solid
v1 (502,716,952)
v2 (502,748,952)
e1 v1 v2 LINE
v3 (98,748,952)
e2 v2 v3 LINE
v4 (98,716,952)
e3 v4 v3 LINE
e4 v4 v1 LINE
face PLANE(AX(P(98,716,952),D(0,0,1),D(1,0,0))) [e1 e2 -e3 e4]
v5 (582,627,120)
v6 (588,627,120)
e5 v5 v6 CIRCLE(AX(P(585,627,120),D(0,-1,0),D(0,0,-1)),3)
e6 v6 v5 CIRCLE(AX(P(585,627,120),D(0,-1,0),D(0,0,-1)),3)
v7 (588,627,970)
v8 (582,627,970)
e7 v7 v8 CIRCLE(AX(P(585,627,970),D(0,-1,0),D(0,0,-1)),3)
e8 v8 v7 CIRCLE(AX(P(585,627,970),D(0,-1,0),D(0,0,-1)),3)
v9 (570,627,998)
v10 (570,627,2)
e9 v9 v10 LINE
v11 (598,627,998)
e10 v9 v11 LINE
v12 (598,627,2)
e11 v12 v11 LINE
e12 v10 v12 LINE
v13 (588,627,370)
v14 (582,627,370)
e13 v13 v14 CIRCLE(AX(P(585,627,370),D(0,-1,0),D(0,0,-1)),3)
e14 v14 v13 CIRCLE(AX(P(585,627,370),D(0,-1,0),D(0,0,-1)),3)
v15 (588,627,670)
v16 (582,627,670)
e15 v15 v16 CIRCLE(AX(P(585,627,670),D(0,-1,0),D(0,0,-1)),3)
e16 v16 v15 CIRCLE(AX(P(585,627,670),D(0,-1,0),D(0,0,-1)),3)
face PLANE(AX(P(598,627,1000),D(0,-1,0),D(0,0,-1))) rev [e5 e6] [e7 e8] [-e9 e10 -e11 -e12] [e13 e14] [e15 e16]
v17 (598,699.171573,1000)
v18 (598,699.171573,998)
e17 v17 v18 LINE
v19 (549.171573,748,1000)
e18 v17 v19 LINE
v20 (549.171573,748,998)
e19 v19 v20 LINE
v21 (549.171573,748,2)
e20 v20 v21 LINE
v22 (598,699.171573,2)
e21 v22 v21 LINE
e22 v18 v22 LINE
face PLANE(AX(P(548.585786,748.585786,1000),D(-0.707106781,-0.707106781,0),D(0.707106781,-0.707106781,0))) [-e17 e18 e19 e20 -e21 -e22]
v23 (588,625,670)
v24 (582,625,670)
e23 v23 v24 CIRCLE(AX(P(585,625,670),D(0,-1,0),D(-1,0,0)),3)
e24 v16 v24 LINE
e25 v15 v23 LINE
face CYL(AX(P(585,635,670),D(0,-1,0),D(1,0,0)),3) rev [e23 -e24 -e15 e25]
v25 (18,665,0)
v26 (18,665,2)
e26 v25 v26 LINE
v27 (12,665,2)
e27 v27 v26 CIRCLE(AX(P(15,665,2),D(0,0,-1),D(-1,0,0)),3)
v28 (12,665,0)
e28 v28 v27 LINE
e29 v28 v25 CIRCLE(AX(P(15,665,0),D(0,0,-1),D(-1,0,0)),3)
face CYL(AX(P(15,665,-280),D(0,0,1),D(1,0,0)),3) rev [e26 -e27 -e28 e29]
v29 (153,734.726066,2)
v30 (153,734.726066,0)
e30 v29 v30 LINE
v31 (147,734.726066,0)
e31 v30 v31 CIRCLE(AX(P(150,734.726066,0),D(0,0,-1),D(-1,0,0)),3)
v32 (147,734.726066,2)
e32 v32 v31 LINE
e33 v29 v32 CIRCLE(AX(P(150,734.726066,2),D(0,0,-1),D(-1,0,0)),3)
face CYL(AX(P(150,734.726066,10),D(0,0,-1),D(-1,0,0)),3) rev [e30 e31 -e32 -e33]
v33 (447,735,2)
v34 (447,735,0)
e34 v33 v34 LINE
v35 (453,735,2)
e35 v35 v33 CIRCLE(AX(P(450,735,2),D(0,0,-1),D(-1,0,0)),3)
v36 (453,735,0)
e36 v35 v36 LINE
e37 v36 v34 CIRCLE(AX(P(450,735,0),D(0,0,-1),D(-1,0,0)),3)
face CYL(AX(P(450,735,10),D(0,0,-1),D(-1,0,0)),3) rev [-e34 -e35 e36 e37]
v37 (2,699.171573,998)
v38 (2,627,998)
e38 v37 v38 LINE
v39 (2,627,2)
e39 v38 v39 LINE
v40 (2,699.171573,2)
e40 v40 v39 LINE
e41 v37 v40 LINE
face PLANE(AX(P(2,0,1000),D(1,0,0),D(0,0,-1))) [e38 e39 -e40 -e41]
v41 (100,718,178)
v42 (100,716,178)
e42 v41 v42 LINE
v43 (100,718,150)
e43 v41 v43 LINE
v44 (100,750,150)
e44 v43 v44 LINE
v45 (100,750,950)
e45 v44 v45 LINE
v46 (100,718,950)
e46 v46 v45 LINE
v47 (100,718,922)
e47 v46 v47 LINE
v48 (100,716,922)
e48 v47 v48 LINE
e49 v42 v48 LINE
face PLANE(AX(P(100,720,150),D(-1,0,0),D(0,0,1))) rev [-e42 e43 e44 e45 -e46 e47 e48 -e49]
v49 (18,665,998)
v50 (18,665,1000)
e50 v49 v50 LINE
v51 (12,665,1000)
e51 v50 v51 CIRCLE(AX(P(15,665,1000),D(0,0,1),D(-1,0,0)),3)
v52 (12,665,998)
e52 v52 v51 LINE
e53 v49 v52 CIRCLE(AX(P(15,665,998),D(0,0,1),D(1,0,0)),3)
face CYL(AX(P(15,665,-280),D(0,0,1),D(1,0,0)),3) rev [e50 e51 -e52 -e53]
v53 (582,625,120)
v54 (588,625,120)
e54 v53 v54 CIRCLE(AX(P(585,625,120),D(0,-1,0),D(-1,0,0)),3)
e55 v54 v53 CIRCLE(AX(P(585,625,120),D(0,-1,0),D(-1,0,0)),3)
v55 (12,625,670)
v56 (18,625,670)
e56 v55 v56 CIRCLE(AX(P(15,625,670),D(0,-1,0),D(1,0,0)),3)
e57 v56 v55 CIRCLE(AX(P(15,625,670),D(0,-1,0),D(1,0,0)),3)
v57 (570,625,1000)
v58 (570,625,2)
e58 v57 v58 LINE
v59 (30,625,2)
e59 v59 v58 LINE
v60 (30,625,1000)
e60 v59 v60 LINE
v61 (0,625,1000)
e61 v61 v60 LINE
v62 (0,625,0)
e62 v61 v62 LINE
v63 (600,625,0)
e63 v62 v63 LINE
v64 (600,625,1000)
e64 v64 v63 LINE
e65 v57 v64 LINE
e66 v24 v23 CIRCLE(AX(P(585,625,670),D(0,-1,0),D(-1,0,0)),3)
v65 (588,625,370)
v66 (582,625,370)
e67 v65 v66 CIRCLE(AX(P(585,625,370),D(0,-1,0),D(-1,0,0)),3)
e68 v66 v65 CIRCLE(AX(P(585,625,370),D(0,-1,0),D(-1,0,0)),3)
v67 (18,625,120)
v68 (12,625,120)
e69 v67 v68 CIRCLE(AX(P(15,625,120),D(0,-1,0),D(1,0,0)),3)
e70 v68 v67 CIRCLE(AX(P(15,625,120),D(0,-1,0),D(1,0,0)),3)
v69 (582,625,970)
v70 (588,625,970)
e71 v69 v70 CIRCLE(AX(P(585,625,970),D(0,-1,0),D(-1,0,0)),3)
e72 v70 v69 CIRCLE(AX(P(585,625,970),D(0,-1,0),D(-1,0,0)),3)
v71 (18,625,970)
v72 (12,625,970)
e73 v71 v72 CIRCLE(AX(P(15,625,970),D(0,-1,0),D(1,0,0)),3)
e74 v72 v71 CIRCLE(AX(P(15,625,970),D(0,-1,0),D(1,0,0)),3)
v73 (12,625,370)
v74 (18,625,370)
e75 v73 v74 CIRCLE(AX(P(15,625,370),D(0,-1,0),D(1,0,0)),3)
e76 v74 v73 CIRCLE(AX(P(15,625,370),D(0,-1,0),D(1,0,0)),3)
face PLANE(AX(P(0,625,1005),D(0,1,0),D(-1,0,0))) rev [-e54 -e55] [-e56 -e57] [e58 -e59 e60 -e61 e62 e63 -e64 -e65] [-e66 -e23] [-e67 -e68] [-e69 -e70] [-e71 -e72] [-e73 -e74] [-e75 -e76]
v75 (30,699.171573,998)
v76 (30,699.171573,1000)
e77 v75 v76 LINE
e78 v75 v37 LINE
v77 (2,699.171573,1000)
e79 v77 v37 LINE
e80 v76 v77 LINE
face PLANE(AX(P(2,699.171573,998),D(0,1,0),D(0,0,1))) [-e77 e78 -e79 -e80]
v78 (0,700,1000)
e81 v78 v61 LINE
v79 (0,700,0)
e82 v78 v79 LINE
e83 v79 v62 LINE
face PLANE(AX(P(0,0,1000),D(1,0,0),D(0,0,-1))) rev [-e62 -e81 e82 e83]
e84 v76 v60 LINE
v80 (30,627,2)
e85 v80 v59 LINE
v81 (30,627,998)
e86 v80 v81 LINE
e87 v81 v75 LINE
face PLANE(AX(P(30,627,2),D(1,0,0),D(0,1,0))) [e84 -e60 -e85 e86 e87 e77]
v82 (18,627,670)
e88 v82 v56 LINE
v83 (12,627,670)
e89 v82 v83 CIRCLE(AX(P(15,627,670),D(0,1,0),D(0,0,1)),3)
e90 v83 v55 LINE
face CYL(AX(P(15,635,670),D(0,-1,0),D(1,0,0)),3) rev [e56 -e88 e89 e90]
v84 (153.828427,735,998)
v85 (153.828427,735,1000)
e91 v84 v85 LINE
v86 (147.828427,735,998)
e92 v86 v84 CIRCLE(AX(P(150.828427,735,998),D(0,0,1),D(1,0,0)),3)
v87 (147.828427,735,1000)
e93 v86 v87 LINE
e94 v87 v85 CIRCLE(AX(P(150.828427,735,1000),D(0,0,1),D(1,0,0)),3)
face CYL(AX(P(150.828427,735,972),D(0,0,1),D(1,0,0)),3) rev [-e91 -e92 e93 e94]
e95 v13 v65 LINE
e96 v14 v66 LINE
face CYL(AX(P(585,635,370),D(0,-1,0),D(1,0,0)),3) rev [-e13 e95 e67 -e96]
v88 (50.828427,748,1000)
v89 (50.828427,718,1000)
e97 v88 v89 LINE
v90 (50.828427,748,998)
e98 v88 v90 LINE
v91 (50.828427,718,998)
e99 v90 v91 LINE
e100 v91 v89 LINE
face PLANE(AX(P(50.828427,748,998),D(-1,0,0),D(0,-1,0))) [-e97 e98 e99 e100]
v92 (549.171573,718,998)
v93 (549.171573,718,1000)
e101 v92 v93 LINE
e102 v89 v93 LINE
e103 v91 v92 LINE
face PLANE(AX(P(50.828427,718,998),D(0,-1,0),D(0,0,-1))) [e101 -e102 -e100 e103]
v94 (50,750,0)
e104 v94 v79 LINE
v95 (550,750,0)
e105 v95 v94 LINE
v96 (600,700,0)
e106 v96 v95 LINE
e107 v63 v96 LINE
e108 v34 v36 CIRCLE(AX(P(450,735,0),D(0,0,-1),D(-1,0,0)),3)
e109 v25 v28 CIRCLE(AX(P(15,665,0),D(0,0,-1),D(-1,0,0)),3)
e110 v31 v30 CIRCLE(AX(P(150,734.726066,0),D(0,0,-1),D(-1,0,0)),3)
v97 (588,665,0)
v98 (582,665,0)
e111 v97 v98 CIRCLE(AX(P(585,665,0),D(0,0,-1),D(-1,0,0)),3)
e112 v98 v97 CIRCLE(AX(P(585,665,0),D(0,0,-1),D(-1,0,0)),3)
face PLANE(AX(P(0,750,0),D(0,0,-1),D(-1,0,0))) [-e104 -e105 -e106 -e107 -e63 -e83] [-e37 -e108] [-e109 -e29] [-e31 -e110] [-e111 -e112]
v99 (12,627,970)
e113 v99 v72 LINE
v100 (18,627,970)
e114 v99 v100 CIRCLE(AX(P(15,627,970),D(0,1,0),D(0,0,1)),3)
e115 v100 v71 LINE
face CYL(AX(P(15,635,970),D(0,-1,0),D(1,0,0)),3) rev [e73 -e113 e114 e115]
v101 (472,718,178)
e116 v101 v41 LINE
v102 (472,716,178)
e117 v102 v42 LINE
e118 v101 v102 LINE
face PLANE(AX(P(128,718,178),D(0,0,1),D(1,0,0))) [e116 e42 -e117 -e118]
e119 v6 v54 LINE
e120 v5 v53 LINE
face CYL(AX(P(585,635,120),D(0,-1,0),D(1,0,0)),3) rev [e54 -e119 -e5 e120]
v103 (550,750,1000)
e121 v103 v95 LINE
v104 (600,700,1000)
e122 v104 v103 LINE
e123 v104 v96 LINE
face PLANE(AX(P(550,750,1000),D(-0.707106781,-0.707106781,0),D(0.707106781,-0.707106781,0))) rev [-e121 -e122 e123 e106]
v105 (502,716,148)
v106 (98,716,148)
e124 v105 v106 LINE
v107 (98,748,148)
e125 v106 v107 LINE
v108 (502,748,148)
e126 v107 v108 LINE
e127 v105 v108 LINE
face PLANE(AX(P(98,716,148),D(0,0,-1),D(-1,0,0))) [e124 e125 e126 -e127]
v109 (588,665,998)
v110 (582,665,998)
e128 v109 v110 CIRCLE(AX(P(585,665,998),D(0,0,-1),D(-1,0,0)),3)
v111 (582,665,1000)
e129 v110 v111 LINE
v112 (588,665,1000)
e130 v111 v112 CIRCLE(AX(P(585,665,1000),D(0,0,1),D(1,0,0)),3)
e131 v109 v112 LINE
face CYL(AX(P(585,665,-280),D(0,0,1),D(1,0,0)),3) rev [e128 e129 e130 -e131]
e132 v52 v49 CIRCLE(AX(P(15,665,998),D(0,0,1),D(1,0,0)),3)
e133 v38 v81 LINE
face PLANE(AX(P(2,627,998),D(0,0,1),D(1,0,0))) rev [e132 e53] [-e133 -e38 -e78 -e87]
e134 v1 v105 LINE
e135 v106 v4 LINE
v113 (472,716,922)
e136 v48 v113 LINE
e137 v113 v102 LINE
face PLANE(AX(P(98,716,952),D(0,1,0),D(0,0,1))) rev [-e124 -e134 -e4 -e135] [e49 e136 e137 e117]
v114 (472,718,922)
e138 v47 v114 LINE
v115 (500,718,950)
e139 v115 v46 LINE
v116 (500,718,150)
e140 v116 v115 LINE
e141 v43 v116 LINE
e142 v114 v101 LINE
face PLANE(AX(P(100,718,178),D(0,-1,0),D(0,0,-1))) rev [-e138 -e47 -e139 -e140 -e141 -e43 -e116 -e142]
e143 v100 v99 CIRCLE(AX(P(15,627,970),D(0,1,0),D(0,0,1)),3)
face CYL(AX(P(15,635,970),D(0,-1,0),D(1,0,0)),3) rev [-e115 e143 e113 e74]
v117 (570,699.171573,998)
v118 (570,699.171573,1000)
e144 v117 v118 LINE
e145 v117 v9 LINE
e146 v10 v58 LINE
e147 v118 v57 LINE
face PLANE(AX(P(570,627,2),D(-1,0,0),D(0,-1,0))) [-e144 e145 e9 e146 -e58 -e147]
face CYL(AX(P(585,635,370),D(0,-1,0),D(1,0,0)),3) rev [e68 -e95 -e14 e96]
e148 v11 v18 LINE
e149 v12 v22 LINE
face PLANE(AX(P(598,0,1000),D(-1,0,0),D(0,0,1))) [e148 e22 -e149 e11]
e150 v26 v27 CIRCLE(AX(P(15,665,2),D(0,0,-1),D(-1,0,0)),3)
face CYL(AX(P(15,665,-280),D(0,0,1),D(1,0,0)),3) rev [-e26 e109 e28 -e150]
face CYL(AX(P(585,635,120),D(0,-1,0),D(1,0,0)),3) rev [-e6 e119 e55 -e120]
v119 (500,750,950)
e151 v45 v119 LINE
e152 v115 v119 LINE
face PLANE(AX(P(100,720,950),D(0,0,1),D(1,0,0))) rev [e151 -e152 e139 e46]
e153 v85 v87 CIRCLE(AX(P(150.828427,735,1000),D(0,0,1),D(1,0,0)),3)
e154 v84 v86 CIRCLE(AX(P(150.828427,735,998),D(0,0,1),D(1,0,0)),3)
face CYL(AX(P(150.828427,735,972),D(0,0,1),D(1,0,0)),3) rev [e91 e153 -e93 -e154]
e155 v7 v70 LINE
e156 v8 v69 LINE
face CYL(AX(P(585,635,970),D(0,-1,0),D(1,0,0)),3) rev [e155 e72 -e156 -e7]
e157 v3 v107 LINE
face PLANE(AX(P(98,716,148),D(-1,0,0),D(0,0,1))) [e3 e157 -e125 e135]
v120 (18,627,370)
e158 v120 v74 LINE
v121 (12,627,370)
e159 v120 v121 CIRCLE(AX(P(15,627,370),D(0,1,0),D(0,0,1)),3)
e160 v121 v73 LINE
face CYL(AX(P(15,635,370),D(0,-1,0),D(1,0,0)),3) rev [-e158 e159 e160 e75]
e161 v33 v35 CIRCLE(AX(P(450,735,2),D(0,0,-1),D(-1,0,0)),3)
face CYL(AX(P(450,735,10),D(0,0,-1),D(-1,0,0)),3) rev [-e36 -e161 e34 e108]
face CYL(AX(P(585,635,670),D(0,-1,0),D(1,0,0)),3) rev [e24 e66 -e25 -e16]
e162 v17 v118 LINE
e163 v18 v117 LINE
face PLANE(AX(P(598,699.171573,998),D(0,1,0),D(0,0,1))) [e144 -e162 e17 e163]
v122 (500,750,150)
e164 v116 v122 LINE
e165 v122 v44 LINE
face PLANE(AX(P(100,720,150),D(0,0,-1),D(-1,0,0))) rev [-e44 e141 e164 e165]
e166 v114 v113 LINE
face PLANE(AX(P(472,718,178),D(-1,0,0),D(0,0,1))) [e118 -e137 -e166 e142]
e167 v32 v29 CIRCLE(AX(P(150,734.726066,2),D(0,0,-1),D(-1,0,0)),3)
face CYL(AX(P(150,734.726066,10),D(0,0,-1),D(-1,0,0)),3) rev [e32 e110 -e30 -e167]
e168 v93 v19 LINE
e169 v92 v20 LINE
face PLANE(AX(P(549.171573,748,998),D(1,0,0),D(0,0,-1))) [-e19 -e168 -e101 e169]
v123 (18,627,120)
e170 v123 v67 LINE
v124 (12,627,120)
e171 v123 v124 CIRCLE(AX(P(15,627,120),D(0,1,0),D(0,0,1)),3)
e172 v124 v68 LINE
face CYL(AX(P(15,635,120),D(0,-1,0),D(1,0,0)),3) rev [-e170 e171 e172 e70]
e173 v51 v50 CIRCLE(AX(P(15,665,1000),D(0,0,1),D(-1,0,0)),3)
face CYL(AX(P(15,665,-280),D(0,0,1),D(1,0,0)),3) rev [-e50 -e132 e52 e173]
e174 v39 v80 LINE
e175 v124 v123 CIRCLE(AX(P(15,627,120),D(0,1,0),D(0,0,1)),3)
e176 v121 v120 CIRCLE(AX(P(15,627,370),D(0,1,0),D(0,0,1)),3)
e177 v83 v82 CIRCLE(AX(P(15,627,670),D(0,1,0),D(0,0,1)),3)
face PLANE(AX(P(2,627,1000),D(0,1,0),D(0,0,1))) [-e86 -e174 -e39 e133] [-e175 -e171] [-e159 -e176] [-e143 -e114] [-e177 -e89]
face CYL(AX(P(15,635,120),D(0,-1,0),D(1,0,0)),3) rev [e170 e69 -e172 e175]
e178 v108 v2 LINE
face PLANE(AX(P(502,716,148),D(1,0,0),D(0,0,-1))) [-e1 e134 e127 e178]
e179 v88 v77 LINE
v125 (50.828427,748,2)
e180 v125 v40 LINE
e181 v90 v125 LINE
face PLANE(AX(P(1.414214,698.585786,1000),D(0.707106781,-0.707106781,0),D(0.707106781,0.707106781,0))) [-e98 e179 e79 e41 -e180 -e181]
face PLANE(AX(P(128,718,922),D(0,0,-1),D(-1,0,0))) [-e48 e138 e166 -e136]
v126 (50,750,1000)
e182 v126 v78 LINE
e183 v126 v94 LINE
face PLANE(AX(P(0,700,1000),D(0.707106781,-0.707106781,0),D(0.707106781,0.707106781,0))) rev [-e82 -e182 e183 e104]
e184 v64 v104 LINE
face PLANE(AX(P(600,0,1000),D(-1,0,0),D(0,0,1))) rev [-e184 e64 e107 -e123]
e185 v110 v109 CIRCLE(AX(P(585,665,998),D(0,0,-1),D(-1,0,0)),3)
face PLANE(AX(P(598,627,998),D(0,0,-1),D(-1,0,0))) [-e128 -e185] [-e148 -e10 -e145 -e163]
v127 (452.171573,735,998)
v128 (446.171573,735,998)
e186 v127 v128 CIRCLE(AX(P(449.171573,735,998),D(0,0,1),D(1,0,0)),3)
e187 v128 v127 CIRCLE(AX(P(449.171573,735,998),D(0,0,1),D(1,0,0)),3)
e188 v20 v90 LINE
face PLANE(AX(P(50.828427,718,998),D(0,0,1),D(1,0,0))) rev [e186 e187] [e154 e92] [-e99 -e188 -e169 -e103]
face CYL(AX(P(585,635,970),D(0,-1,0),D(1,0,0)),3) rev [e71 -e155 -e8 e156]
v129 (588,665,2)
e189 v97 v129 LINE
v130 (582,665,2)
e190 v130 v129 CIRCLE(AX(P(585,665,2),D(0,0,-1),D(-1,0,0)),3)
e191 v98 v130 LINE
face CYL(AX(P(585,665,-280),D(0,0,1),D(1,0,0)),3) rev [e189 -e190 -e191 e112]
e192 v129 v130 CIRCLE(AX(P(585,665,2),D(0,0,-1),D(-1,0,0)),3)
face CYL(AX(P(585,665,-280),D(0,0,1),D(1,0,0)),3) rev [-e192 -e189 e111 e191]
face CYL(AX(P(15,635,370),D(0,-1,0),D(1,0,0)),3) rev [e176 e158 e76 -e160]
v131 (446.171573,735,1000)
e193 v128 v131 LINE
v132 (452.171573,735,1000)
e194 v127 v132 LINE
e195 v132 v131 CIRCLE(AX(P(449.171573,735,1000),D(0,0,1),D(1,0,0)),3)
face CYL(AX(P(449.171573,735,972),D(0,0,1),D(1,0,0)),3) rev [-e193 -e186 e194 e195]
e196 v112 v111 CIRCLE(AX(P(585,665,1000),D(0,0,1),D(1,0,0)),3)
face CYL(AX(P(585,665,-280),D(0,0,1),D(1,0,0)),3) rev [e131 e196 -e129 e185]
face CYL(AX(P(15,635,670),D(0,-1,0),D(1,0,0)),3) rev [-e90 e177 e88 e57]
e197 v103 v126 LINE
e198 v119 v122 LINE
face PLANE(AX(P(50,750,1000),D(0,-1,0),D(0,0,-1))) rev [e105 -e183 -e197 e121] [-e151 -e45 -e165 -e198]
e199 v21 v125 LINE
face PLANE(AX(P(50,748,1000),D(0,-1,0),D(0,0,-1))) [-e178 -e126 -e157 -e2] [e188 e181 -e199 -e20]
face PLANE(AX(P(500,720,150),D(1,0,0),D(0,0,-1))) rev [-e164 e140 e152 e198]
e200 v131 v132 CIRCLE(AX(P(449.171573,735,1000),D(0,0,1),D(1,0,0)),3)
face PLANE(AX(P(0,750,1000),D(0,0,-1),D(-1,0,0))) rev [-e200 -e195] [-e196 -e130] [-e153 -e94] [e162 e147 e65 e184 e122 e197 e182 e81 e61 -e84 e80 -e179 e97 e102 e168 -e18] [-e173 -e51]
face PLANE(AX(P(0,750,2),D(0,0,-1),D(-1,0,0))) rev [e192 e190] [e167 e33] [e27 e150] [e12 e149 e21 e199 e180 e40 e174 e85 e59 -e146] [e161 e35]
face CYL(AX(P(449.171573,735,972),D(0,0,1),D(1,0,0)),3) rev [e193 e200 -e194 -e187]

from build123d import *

# Parameters (mm, degrees)
EXTRUDE_1_DEPTH     = 1000
SHELL_1_T           = -2
SKETCH_3_W          = 400
SKETCH_3_H          = 800
CUT_EXTRUDE_1_DEPTH = 30
SKETCH_4_W          = 404
SKETCH_4_H          = 804
SKETCH_4_W_2        = 400
SKETCH_4_H_2        = 800
EXTRUDE_2_DEPTH     = 34
EXTRUDE_3_DEPTH     = 2
SKETCH_6_W          = 600
SKETCH_6_H          = 200
CUT_EXTRUDE_2_DEPTH = 1044
SKETCH_10_W         = 600
SKETCH_10_H         = 425
CUT_EXTRUDE_4_DEPTH = 1005
SKETCH_11_W         = 28
SKETCH_11_H         = 998
EXTRUDE_5_DEPTH     = 2
SKETCH_12_W         = 498.34314575
SKETCH_12_H         = 30
SKETCH_12_W_2       = 28
SKETCH_12_H_2       = 72.171572875
EXTRUDE_6_DEPTH     = 2
SKETCH_13_R         = 3
CUT_EXTRUDE_5_DEPTH = 1280
SKETCH_14_R         = 3
CUT_EXTRUDE_6_DEPTH = 10
SKETCH_15_R         = 3
CUT_EXTRUDE_7_DEPTH = 28
SKETCH_16_R         = 3
CUT_EXTRUDE_8_DEPTH = 10


with BuildPart() as part:
    # 草图1 → 凸台-拉伸1 (new body)
    with BuildSketch(Plane.XY):
        Polygon((0, 700), (50, 750), (550, 750), (600, 700), (600, 0), (0, 0), align=None)
    extrude(amount=EXTRUDE_1_DEPTH)

    # 抽壳1
    shell_1_openings = [part.faces().sort_by_distance(p)[0] for p in [
        (300, 372.998137803, 1000),
    ]]
    offset(amount=SHELL_1_T, openings=shell_1_openings, kind=Kind.INTERSECTION)

    # 草图3 → 切除-拉伸1 (cut)
    with BuildSketch(Plane(origin=(0, 750, 0), x_dir=(1, 0, 0), z_dir=(0, 1, 0))):
        with Locations((300, -550)):
            Rectangle(SKETCH_3_W, SKETCH_3_H)
    extrude(amount=-CUT_EXTRUDE_1_DEPTH, mode=Mode.SUBTRACT)

    # 草图4 → 凸台-拉伸2 (add)
    with BuildSketch(Plane(origin=(0, 750, 0), x_dir=(1, 0, 0), z_dir=(0, 1, 0))):
        with Locations((300, -550)):
            Rectangle(SKETCH_4_W, SKETCH_4_H)
        with Locations((300, -550)):
            Rectangle(SKETCH_4_W_2, SKETCH_4_H_2, mode=Mode.SUBTRACT)
    extrude(amount=-EXTRUDE_2_DEPTH)

    # 草图5 → 凸台-拉伸3 (add)
    with BuildSketch(Plane.XZ.offset(-716)):
        Polygon((128, 178), (472, 178), (472, 922), (128, 922), (100, 922), (100, 950), (500, 950), (500, 150), (100, 150), (100, 178), align=None)
    extrude(amount=-EXTRUDE_3_DEPTH)

    # 草图6 → 切除-拉伸2 (cut)
    with BuildSketch(Plane(origin=(0, 0, 0), x_dir=(-1, 0, 0), z_dir=(0, 0, -1))):
        with Locations((-300, 100)):
            Rectangle(SKETCH_6_W, SKETCH_6_H)
    extrude(amount=-CUT_EXTRUDE_2_DEPTH, mode=Mode.SUBTRACT)

    # 草图10 → 切除-拉伸4 (cut)
    with BuildSketch(Plane(origin=(0, 0, 0), x_dir=(-1, 0, 0), z_dir=(0, 0, -1))):
        with Locations((-300, 412.5)):
            Rectangle(SKETCH_10_W, SKETCH_10_H)
    extrude(amount=-CUT_EXTRUDE_4_DEPTH, mode=Mode.SUBTRACT)

    # 草图11 → 凸台-拉伸5 (add)
    with BuildSketch(Plane.XZ.offset(-625)):
        with Locations((16, 501)):
            Rectangle(SKETCH_11_W, SKETCH_11_H)
        with Locations((584, 501)):
            Rectangle(SKETCH_11_W, SKETCH_11_H)
    extrude(amount=-EXTRUDE_5_DEPTH)

    # 草图12 → 凸台-拉伸6 (add)
    with BuildSketch(Plane.XY.offset(1000)):
        with Locations((300, 733)):
            Rectangle(SKETCH_12_W, SKETCH_12_H)
        with Locations((16, 663.085786438)):
            Rectangle(SKETCH_12_W_2, SKETCH_12_H_2)
        with Locations((584, 663.085786438)):
            Rectangle(SKETCH_12_W_2, SKETCH_12_H_2)
    extrude(amount=-EXTRUDE_6_DEPTH)

    # 草图13 → 切除-拉伸5 (cut)
    with BuildSketch(Plane.XY.offset(1000)):
        with Locations((585, 665)):
            Circle(SKETCH_13_R)
        with Locations((15, 665)):
            Circle(SKETCH_13_R)
    extrude(amount=-CUT_EXTRUDE_5_DEPTH, mode=Mode.SUBTRACT)

    # 草图14 → 切除-拉伸6 (cut)
    with BuildSketch(Plane.XZ.offset(-625)):
        with Locations((15, 970)):
            Circle(SKETCH_14_R)
        with Locations((15, 670)):
            Circle(SKETCH_14_R)
        with Locations(Location((585, 120, 0), (0, 0, 270))):
            Circle(SKETCH_14_R)
        with Locations((15, 370)):
            Circle(SKETCH_14_R)
        with Locations(Location((585, 370, 0), (0, 0, 270))):
            Circle(SKETCH_14_R)
        with Locations((15, 120)):
            Circle(SKETCH_14_R)
        with Locations(Location((585, 670, 0), (0, 0, 270))):
            Circle(SKETCH_14_R)
        with Locations(Location((585, 970, 0), (0, 0, 270))):
            Circle(SKETCH_14_R)
    extrude(amount=-CUT_EXTRUDE_6_DEPTH, mode=Mode.SUBTRACT)

    # 草图15 → 切除-拉伸7 (cut)
    with BuildSketch(Plane.XY.offset(1000)):
        with Locations((150.828427125, 735)):
            Circle(SKETCH_15_R)
        with Locations((449.171572875, 735)):
            Circle(SKETCH_15_R)
    extrude(amount=-CUT_EXTRUDE_7_DEPTH, mode=Mode.SUBTRACT)

    # 草图16 → 切除-拉伸8 (cut)
    with BuildSketch(Plane(origin=(0, 0, 0), x_dir=(-1, 0, 0), z_dir=(0, 0, -1))):
        with Locations((-450, 735)):
            Circle(SKETCH_16_R)
        with Locations((-150, 734.726066428)):
            Circle(SKETCH_16_R)
    extrude(amount=-CUT_EXTRUDE_8_DEPTH, mode=Mode.SUBTRACT)


solid = part.part
